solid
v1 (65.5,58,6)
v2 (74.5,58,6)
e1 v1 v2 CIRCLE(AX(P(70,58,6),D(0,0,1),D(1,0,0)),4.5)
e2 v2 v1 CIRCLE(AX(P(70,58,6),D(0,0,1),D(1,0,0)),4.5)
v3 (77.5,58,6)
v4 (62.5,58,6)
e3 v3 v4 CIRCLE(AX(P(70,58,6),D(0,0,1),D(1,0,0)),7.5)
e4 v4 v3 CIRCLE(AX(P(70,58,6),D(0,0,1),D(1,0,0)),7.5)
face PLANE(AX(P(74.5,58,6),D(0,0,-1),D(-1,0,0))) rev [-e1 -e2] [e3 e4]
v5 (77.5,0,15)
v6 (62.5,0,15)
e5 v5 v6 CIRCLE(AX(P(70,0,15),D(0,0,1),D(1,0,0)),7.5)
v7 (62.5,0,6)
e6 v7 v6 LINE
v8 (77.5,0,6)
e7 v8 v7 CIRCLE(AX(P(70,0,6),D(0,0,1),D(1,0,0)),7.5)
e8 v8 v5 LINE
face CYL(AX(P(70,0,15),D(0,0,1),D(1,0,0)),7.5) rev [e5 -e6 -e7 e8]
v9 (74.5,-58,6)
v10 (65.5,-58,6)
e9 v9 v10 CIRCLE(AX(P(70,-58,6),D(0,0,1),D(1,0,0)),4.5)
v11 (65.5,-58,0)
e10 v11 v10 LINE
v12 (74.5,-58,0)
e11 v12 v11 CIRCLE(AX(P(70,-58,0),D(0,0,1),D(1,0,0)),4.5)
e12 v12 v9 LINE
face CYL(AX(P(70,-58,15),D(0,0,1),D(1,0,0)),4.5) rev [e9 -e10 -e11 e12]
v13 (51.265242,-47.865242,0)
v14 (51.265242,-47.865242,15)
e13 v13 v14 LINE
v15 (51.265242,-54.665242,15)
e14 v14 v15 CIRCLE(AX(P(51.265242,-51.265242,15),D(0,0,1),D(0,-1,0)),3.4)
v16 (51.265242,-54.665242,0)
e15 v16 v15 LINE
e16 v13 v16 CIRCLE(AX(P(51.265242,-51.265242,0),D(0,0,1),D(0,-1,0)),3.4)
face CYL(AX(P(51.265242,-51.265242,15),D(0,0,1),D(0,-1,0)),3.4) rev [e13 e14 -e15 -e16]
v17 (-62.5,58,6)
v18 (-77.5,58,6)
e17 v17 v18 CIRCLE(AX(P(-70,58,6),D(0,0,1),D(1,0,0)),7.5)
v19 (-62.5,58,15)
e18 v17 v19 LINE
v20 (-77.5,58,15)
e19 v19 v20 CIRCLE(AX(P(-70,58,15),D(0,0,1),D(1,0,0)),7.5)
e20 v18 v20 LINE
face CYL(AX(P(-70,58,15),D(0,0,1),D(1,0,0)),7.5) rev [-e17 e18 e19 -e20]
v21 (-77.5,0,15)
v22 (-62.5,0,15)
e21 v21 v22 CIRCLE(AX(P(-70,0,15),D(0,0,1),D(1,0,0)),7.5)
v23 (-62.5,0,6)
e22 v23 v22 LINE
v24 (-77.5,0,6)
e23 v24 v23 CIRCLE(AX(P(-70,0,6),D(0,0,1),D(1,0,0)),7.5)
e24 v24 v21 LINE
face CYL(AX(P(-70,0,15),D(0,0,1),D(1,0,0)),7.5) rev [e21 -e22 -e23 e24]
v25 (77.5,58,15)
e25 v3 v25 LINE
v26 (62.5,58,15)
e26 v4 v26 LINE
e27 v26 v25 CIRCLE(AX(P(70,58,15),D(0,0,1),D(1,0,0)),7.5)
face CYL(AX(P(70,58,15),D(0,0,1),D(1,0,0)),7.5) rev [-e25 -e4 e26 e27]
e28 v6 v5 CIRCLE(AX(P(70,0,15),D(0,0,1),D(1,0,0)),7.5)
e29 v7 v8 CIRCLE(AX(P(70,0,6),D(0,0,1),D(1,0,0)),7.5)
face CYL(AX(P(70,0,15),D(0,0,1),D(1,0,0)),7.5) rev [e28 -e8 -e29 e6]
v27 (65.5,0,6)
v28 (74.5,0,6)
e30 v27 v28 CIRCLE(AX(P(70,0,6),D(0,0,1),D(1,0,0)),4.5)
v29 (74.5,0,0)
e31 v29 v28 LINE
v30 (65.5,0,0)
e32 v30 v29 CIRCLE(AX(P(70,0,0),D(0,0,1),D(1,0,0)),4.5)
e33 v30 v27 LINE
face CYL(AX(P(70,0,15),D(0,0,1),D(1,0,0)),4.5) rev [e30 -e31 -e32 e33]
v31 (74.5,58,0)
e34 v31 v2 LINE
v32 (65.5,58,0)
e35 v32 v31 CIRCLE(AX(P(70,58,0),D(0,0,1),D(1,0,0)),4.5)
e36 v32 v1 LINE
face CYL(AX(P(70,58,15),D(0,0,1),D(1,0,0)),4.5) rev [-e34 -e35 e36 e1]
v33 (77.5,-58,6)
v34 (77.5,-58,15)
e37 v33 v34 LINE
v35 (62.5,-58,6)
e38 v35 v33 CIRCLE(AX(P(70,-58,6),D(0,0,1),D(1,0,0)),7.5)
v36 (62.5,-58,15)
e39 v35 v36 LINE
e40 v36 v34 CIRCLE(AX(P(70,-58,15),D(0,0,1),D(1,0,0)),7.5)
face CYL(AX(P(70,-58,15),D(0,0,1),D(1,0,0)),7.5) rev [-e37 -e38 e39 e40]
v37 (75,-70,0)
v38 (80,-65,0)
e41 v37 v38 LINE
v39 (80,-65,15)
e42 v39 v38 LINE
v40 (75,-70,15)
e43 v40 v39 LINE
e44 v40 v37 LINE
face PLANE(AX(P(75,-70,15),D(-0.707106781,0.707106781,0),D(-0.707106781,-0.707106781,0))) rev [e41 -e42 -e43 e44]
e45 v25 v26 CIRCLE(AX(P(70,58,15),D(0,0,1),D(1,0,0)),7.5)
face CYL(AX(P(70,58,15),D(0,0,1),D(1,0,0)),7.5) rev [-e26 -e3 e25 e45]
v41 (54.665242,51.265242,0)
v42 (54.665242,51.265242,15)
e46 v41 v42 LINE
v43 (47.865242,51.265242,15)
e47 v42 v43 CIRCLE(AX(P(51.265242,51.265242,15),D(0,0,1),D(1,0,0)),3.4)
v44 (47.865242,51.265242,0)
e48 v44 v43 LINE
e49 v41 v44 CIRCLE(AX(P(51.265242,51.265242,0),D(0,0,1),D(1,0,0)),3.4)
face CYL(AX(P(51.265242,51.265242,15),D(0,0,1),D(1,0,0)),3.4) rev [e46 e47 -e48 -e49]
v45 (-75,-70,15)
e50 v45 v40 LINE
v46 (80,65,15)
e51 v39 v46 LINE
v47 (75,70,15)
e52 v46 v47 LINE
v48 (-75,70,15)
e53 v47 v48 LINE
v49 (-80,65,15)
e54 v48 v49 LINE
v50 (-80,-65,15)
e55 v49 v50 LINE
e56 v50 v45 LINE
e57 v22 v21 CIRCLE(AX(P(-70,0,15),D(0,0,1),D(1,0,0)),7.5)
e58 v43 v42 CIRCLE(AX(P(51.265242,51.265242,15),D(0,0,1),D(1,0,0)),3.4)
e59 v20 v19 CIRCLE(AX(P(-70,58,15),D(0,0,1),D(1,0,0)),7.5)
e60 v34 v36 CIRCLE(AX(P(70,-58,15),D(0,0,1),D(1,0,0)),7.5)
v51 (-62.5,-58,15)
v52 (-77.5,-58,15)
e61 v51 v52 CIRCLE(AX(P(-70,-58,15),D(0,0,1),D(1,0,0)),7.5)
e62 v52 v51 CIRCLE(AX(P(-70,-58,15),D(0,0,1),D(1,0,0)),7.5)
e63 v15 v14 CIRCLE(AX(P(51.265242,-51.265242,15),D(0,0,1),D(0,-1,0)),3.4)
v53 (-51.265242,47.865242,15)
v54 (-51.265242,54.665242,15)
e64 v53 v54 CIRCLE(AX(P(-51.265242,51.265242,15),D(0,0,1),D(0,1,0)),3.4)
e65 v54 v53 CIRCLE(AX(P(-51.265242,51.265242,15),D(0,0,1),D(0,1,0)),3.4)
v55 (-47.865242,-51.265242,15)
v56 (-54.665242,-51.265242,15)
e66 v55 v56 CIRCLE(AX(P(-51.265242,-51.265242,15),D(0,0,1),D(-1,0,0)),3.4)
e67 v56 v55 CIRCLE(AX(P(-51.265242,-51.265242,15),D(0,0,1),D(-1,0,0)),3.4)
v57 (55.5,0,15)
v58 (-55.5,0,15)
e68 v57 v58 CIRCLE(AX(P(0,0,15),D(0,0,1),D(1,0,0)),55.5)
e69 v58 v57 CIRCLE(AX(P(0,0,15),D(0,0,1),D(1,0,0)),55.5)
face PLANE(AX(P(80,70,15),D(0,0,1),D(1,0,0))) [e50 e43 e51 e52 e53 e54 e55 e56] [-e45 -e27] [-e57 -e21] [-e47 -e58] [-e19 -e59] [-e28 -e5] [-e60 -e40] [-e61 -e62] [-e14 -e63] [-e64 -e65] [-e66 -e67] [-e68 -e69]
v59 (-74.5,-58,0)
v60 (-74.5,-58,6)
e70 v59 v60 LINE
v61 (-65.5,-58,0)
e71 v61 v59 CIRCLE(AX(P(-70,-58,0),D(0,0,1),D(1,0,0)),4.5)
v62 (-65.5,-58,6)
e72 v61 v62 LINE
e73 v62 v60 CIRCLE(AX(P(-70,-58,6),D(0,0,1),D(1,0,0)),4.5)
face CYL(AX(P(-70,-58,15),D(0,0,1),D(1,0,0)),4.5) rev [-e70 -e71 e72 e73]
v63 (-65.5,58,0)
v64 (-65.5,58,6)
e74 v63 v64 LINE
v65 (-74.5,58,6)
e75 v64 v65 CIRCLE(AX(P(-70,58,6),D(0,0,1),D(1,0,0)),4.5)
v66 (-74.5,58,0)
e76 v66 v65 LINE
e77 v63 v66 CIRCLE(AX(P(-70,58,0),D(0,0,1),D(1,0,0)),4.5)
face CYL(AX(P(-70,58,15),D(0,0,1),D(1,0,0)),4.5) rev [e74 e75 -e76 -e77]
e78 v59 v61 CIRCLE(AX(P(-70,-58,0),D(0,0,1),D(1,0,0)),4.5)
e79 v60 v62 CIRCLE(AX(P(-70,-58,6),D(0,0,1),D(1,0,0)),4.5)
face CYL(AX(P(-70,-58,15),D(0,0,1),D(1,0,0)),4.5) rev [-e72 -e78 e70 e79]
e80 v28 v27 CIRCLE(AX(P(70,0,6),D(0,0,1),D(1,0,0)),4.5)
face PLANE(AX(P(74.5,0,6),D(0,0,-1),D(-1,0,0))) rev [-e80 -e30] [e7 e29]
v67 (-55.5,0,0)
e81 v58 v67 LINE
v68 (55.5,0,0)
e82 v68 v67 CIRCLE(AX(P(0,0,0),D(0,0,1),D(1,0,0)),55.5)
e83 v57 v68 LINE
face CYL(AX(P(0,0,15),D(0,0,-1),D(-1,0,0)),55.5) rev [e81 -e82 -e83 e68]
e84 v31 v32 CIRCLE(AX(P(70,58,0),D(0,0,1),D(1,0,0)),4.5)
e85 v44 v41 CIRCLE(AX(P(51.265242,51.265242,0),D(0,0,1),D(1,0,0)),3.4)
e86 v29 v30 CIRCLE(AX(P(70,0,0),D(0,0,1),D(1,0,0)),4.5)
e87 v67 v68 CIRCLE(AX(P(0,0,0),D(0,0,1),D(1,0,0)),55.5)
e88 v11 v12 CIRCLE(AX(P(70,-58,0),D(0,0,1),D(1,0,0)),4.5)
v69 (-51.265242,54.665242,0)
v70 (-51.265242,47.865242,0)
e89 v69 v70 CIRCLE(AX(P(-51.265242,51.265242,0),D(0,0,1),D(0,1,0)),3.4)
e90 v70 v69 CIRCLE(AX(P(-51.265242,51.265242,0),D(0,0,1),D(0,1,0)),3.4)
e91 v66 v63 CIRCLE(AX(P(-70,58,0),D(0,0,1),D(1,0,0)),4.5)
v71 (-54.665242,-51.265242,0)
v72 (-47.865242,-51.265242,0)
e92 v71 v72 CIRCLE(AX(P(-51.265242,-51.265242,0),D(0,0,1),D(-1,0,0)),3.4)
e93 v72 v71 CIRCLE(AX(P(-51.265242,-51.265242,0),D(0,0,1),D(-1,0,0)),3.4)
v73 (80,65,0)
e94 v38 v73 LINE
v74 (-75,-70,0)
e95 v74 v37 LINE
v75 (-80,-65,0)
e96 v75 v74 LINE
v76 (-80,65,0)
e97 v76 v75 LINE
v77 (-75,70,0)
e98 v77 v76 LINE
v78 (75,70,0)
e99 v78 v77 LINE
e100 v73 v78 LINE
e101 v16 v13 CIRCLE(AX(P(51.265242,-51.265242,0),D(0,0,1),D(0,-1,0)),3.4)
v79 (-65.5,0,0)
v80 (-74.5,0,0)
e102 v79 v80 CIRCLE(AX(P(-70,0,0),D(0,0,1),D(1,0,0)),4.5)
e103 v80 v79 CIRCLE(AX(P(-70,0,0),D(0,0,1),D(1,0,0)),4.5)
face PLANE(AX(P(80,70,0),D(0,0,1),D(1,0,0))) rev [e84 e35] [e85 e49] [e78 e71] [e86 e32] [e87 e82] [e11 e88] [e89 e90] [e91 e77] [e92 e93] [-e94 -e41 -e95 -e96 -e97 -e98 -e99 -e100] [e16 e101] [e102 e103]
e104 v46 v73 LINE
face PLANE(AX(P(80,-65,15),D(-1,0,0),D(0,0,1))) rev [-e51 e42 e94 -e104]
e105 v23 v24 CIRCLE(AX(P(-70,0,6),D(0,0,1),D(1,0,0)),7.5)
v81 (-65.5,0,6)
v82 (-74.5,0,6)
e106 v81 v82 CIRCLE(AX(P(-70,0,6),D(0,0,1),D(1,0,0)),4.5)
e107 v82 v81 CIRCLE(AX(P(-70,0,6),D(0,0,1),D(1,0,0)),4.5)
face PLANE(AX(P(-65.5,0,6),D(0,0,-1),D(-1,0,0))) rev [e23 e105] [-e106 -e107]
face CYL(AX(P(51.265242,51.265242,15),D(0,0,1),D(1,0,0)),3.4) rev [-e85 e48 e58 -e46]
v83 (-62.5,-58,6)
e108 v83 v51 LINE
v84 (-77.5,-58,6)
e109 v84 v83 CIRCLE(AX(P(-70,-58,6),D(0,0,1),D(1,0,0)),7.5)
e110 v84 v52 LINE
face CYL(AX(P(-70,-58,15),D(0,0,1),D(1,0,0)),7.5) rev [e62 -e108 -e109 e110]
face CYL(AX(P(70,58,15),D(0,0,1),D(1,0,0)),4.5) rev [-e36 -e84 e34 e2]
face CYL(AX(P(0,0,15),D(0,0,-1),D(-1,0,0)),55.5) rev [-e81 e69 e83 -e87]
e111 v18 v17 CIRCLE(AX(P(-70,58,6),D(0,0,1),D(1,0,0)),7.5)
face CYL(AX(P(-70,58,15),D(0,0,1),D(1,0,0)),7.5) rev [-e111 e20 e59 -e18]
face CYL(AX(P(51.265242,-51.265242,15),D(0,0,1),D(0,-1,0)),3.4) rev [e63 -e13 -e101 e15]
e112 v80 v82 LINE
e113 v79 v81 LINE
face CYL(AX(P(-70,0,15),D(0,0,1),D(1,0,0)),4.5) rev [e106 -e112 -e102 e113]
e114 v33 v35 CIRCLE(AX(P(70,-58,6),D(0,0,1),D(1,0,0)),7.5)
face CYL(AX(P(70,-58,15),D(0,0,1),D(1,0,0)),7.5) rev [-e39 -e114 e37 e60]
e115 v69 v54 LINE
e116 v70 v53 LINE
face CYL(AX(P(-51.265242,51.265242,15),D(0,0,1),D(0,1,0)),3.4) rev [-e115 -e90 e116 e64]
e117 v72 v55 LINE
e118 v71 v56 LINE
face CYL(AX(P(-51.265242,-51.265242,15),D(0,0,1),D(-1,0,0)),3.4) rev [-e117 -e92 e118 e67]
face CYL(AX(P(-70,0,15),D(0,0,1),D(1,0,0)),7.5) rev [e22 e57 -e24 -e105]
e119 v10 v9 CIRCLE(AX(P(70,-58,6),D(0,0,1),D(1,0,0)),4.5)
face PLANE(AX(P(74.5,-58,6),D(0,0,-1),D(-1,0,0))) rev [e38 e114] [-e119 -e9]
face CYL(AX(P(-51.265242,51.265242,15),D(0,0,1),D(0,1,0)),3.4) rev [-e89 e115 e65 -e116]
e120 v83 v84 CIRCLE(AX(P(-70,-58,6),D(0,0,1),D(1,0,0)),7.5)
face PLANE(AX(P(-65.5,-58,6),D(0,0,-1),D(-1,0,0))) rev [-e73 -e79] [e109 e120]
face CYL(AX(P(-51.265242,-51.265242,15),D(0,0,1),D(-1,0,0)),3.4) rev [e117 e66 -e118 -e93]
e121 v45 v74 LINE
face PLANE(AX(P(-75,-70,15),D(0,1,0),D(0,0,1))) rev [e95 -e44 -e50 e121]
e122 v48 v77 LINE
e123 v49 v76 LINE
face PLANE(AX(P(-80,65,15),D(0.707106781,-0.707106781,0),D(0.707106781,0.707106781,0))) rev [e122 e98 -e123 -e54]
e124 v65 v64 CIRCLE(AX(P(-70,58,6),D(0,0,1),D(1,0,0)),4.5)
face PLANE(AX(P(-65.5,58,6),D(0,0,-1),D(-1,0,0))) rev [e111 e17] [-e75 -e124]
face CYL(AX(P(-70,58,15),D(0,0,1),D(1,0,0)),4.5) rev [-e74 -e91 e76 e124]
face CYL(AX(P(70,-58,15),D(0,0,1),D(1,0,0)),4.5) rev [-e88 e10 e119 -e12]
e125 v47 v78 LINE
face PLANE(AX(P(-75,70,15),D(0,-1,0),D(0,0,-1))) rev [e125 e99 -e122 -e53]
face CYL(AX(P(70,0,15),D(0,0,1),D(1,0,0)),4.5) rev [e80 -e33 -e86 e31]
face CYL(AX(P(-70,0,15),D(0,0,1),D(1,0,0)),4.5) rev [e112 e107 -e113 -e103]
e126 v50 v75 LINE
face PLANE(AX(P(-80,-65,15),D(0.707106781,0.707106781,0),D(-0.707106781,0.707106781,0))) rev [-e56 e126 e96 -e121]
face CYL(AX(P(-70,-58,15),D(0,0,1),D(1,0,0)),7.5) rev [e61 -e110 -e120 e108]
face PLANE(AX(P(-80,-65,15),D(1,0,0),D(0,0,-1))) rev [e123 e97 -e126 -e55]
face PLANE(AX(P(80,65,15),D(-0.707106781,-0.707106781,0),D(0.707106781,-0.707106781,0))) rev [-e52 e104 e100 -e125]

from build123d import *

# Parameters (mm, degrees)
SKETCH1_R                                            = 55.5
BOSS_EXTRUDE1_DEPTH                                  = 15
CIRPATTERN1_COUNT                                    = 4
HOLE_SIZE_PER_SOCKET_HEAD_CAP_SCREW_TYPE_D           = 9
HOLE_SIZE_PER_SOCKET_HEAD_CAP_SCREW_TYPE_CBORE_D     = 15
HOLE_SIZE_PER_SOCKET_HEAD_CAP_SCREW_TYPE_CBORE_DEPTH = 9


with BuildPart() as part:
    # Sketch1 → Boss-Extrude1 (new body)
    with BuildSketch(Plane.XY):
        Polygon((-80, 65), (-75, 70), (75, 70), (80, 65), (80, -65), (75, -70), (-75, -70), (-80, -65), align=None)
        Circle(SKETCH1_R, mode=Mode.SUBTRACT)
    extrude(amount=BOSS_EXTRUDE1_DEPTH)

    # Sketch2 → M8 Tapped Hole1 (revolve, cut)
    with BuildSketch(Plane(origin=(51.265241636, 51.265241636, 15), x_dir=(0, -1, 0), z_dir=(1, 0, 0))):
        Polygon((0, 0), (0, 21.792926105), (3.4, 19.75), (3.4, 0), align=None)
    m8_tapped_hole1 = revolve(axis=Axis((51.265241636, 51.265241636, 21.35), (0, 0, -1)), mode=Mode.SUBTRACT)

    # CirPattern1: M8 Tapped Hole1 ×4 about axis
    cirpattern1_axis = Axis((0, 0, 0), (0, 0, 1))
    for i in range(1, CIRPATTERN1_COUNT):
        add(m8_tapped_hole1.rotate(cirpattern1_axis, i * 360 / CIRPATTERN1_COUNT), mode=Mode.SUBTRACT)

    # Hole size per socket head cap screw type1 (through all)
    with Locations(Plane(origin=(37.833357844, 52.116019714, 15), x_dir=(-1, 0, 0), z_dir=(0, 0, 1))):
        with Locations((-32.166642156, -5.883980286), (-32.166642156, 52.116019714), (-32.166642156, 110.116019714)):
            hole_size_per_socket_head_cap_screw_type = CounterBoreHole(HOLE_SIZE_PER_SOCKET_HEAD_CAP_SCREW_TYPE_D / 2, HOLE_SIZE_PER_SOCKET_HEAD_CAP_SCREW_TYPE_CBORE_D / 2, HOLE_SIZE_PER_SOCKET_HEAD_CAP_SCREW_TYPE_CBORE_DEPTH)

    # Mirror1: Hole size per socket head cap screw type1 across plane
    add(hole_size_per_socket_head_cap_screw_type.mirror(Plane(origin=(0, 0, 0), x_dir=(0, 0, 1), z_dir=(1, 0, 0))), mode=Mode.SUBTRACT)


solid = part.part
